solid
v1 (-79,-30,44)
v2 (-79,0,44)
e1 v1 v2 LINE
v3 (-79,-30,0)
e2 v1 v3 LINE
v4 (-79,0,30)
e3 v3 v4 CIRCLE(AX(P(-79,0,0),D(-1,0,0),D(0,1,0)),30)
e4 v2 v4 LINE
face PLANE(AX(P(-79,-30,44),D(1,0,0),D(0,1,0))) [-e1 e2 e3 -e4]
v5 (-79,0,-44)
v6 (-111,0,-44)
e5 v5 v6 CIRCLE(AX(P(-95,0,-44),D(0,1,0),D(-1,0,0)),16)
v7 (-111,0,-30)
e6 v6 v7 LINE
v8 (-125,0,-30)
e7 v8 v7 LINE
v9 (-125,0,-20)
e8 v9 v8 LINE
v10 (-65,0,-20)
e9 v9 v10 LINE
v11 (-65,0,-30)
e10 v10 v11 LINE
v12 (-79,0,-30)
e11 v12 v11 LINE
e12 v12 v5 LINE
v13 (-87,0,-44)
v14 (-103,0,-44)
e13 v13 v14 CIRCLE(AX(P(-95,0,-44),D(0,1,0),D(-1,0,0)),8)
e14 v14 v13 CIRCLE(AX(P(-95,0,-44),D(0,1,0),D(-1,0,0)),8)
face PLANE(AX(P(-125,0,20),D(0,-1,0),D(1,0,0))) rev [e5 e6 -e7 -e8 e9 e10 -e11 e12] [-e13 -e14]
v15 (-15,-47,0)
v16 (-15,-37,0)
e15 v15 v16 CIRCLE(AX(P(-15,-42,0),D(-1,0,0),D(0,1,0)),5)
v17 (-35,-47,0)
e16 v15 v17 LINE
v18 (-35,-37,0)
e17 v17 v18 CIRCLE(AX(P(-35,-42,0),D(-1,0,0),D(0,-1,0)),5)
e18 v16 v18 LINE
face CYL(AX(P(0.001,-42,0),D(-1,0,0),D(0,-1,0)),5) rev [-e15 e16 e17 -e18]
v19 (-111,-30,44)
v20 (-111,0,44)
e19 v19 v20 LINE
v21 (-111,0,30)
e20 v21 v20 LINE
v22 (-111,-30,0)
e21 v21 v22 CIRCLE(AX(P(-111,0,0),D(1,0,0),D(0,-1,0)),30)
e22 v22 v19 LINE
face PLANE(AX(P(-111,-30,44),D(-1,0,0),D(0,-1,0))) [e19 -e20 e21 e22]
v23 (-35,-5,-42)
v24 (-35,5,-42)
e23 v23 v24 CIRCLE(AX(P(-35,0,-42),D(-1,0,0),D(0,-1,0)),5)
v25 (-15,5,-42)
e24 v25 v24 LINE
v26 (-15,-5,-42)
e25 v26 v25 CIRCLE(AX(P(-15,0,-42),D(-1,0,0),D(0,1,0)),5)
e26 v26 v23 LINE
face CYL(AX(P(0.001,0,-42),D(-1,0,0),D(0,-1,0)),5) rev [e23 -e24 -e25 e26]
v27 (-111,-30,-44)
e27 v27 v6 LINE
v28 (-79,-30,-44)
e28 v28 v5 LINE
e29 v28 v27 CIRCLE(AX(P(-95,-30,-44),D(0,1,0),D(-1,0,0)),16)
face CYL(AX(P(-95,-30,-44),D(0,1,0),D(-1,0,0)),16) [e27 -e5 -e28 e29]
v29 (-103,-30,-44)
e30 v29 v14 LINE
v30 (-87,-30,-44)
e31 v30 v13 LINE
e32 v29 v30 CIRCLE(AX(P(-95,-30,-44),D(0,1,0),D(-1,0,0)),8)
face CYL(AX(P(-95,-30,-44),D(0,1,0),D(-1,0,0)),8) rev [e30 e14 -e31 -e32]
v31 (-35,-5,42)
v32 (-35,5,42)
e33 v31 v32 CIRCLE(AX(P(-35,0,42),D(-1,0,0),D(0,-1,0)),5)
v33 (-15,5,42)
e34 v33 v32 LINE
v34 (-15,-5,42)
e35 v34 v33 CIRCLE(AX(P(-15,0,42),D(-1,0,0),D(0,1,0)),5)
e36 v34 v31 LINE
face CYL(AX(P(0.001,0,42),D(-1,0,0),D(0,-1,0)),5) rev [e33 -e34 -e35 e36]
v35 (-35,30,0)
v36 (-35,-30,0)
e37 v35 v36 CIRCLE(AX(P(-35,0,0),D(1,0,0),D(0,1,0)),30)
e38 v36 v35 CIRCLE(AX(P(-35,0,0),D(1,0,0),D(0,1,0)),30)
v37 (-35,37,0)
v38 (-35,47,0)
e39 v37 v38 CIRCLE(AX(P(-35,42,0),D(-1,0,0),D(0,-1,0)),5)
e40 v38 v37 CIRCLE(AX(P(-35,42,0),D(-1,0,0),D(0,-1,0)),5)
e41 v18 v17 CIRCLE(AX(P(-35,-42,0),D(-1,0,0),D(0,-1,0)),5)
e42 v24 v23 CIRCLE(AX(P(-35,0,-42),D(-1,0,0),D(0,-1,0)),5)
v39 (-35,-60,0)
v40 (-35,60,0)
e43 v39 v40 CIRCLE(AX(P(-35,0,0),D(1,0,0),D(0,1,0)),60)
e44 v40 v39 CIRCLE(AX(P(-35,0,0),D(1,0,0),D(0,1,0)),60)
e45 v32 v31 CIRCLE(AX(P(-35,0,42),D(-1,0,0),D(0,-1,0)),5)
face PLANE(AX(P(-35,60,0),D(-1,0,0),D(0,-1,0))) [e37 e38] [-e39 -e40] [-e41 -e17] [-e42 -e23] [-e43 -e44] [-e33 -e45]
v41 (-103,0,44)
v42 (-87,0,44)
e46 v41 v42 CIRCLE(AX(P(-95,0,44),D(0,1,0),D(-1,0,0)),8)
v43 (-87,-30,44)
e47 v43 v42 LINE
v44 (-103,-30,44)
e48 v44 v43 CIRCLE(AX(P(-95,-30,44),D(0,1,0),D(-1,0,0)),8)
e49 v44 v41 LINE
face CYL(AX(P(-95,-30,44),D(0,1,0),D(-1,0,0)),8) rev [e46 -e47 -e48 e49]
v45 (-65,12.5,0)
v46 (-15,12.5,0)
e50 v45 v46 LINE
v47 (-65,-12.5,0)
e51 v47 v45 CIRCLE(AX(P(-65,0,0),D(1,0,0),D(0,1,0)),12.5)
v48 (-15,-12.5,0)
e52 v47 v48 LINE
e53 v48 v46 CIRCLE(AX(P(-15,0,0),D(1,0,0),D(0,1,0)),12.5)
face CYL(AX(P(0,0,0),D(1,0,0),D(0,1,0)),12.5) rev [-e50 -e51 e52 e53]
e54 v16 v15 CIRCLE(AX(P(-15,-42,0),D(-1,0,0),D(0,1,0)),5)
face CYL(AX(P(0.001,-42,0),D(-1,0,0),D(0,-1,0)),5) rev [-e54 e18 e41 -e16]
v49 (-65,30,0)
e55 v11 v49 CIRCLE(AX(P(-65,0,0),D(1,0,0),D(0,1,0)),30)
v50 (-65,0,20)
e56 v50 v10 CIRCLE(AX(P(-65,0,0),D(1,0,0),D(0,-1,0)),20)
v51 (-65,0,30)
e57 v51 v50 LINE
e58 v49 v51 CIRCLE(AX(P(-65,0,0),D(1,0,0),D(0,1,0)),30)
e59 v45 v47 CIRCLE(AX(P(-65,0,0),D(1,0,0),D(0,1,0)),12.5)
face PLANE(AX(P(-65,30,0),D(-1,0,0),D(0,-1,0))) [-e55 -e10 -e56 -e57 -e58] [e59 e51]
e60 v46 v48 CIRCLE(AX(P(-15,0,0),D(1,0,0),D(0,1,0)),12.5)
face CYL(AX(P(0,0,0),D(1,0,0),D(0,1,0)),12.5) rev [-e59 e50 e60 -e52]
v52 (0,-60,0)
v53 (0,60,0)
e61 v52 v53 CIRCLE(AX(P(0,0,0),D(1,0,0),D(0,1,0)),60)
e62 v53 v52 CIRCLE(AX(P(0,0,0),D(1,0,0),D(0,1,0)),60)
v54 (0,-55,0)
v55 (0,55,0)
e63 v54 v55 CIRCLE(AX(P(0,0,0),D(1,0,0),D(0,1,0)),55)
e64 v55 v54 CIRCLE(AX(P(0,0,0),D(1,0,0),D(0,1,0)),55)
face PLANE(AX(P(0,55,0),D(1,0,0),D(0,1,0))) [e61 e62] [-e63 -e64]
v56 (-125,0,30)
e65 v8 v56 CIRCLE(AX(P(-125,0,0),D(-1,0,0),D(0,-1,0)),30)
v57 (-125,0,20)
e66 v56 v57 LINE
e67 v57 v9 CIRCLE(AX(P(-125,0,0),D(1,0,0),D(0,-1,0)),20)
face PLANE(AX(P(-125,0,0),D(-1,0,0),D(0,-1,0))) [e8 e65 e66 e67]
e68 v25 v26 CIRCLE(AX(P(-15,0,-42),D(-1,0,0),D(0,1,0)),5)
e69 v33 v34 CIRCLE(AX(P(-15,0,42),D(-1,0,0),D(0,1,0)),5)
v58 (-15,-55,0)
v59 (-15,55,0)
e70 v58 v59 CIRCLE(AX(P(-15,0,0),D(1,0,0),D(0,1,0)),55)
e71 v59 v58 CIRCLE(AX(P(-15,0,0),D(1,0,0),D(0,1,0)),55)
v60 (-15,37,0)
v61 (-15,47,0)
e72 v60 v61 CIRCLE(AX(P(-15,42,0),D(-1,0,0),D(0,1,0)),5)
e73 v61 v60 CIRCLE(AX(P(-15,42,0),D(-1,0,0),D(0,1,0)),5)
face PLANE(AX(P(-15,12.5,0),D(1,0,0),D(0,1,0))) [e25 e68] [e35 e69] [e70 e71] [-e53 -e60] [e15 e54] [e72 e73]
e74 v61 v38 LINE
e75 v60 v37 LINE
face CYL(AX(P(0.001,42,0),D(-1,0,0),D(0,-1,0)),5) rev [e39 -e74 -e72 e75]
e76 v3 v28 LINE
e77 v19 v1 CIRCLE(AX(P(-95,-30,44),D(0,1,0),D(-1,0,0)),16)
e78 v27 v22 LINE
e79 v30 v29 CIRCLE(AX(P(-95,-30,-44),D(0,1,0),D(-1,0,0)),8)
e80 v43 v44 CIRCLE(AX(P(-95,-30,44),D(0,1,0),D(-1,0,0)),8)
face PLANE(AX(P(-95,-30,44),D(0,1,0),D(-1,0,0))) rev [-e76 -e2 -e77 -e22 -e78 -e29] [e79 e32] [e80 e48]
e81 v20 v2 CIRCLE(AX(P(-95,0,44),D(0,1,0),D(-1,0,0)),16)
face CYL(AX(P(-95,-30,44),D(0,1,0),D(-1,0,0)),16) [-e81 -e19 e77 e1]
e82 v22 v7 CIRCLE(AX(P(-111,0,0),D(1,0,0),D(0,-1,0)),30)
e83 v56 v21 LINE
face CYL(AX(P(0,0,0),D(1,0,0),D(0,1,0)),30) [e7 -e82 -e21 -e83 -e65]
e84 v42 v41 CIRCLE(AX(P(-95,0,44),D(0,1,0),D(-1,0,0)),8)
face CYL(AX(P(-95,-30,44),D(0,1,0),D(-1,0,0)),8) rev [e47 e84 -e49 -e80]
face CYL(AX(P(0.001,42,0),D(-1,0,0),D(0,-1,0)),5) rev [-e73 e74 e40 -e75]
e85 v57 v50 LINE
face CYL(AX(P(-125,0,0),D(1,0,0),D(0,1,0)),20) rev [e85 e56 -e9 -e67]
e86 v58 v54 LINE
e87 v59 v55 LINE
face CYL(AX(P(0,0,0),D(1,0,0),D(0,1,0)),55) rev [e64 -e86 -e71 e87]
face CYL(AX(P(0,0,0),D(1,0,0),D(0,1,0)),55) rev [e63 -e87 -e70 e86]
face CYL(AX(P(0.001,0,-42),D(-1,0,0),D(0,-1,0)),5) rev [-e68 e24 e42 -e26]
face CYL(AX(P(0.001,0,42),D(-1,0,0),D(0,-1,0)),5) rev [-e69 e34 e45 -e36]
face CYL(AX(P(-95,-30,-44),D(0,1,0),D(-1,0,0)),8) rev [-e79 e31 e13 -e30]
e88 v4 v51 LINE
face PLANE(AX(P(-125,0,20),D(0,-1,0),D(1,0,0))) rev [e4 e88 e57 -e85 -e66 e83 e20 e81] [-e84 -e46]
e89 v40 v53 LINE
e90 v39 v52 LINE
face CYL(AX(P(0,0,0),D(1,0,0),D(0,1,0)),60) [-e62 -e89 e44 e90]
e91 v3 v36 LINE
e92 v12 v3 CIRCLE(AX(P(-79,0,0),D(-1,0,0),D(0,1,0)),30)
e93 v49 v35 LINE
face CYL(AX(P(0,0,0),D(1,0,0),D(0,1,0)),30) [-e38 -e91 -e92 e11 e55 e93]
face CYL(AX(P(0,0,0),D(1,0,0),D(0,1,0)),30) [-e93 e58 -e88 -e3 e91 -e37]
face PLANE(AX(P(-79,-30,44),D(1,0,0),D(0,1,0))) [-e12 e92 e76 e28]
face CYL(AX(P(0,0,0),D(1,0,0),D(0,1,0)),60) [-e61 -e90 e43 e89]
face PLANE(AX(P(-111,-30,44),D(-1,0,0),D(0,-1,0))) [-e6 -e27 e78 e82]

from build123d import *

# Parameters (mm, degrees)
FLANGE_BOLT_HOLES_4X_10_REACH = 93.788
FLANGE_BOLT_HOLES_SKETCH_R    = 5
BEARING_START                 = 60
BEARING_BLOCK_DEPTH           = 60
SPLIT_CAP_LUGS_SKETCH_R       = 8
SPLIT_CAP_LUGS_DEPTH          = 30
JOURNAL_SEAT_SPLIT_CUT_REACH  = 141.718


with BuildPart() as part:
    # Flanged Hub Profile → Flanged Hub (revolve)
    with BuildSketch(Plane.XY):
        Polygon((0, 60), (-35, 60), (-35, 30), (-65, 30), (-65, 12.5), (-15, 12.5), (-15, 55), (0, 55), align=None)
    revolve(axis=Axis((0, 0, 0), (-1, 0, 0)))

    # Flange Bolt Holes Sketch → Flange Bolt Holes 4xØ10 (cut, up to next)
    with BuildSketch(Plane.ZY.offset(35), mode=Mode.PRIVATE) as flange_bolt_holes_4x_10_sk1:
        with Locations(Location((42, 0, 0), (0, 0, 270))):
            Circle(FLANGE_BOLT_HOLES_SKETCH_R)
    flange_bolt_holes_4x_10_tool1 = extrude(flange_bolt_holes_4x_10_sk1.sketch, amount=-FLANGE_BOLT_HOLES_4X_10_REACH, mode=Mode.PRIVATE) & part.part
    # Flange Bolt Holes Sketch → Flange Bolt Holes 4xØ10 (cut, up to next)
    with BuildSketch(Plane.ZY.offset(35), mode=Mode.PRIVATE) as flange_bolt_holes_4x_10_sk2:
        with Locations(Location((0, -42, 0), (0, 0, 270))):
            Circle(FLANGE_BOLT_HOLES_SKETCH_R)
    flange_bolt_holes_4x_10_tool2 = extrude(flange_bolt_holes_4x_10_sk2.sketch, amount=-FLANGE_BOLT_HOLES_4X_10_REACH, mode=Mode.PRIVATE) & part.part
    # Flange Bolt Holes Sketch → Flange Bolt Holes 4xØ10 (cut, up to next)
    with BuildSketch(Plane.ZY.offset(35), mode=Mode.PRIVATE) as flange_bolt_holes_4x_10_sk3:
        with Locations(Location((-42, 0, 0), (0, 0, 270))):
            Circle(FLANGE_BOLT_HOLES_SKETCH_R)
    flange_bolt_holes_4x_10_tool3 = extrude(flange_bolt_holes_4x_10_sk3.sketch, amount=-FLANGE_BOLT_HOLES_4X_10_REACH, mode=Mode.PRIVATE) & part.part
    # Flange Bolt Holes Sketch → Flange Bolt Holes 4xØ10 (cut, up to next)
    with BuildSketch(Plane.ZY.offset(35), mode=Mode.PRIVATE) as flange_bolt_holes_4x_10_sk4:
        with Locations(Location((0, 42, 0), (0, 0, 270))):
            Circle(FLANGE_BOLT_HOLES_SKETCH_R)
    flange_bolt_holes_4x_10_tool4 = extrude(flange_bolt_holes_4x_10_sk4.sketch, amount=-FLANGE_BOLT_HOLES_4X_10_REACH, mode=Mode.PRIVATE) & part.part
    add(flange_bolt_holes_4x_10_tool1.solids().sort_by_distance((-35, 0, 42))[0], mode=Mode.SUBTRACT)
    add(flange_bolt_holes_4x_10_tool2.solids().sort_by_distance((-35, -42, 0))[0], mode=Mode.SUBTRACT)
    add(flange_bolt_holes_4x_10_tool3.solids().sort_by_distance((-35, 0, -42))[0], mode=Mode.SUBTRACT)
    add(flange_bolt_holes_4x_10_tool4.solids().sort_by_distance((-35, 42, 0))[0], mode=Mode.SUBTRACT)

    # Bearing Block Sketch → Bearing Block (add)
    with BuildSketch(Plane.ZY.offset(65).offset(BEARING_START)):
        with BuildLine():
            Line((-30, 0), (-20, 0))
            ThreePointArc((-20, 0), (0, -20), (20, 0))
            Line((20, 0), (30, 0))
            ThreePointArc((30, 0), (0, -30), (-30, 0))
        make_face()
    extrude(amount=-BEARING_BLOCK_DEPTH)

    # Split Cap Lugs Sketch → Split Cap Lugs (add)
    with BuildSketch(Plane(origin=(0, 0, 0), x_dir=(1, 0, 0), z_dir=(0, 1, 0))):
        with BuildLine():
            Line((-111, -44), (-111, 44))
            ThreePointArc((-111, 44), (-95, 60), (-79, 44))
            Line((-79, 44), (-79, -44))
            ThreePointArc((-79, -44), (-95, -60), (-111, -44))
        make_face()
        with Locations(Location((-95, 44, 0), (0, 0, 180))):
            Circle(SPLIT_CAP_LUGS_SKETCH_R, mode=Mode.SUBTRACT)
        with Locations(Location((-95, -44, 0), (0, 0, 180))):
            Circle(SPLIT_CAP_LUGS_SKETCH_R, mode=Mode.SUBTRACT)
    extrude(amount=-SPLIT_CAP_LUGS_DEPTH)

    # Journal Seat Split Sketch → Journal Seat Split Cut (cut, up to next)
    with BuildSketch(Plane.ZY.offset(111), mode=Mode.PRIVATE) as journal_seat_split_cut_sk1:
        with BuildLine():
            Line((20, 0), (-20, 0))
            ThreePointArc((-20, 0), (0, -20), (20, 0))
        make_face()
    journal_seat_split_cut_tool1 = extrude(journal_seat_split_cut_sk1.sketch, amount=-JOURNAL_SEAT_SPLIT_CUT_REACH, mode=Mode.PRIVATE) & part.part
    add(journal_seat_split_cut_tool1.solids().sort_by_distance((-111, -8.488264, 0))[0], mode=Mode.SUBTRACT)


solid = part.part
